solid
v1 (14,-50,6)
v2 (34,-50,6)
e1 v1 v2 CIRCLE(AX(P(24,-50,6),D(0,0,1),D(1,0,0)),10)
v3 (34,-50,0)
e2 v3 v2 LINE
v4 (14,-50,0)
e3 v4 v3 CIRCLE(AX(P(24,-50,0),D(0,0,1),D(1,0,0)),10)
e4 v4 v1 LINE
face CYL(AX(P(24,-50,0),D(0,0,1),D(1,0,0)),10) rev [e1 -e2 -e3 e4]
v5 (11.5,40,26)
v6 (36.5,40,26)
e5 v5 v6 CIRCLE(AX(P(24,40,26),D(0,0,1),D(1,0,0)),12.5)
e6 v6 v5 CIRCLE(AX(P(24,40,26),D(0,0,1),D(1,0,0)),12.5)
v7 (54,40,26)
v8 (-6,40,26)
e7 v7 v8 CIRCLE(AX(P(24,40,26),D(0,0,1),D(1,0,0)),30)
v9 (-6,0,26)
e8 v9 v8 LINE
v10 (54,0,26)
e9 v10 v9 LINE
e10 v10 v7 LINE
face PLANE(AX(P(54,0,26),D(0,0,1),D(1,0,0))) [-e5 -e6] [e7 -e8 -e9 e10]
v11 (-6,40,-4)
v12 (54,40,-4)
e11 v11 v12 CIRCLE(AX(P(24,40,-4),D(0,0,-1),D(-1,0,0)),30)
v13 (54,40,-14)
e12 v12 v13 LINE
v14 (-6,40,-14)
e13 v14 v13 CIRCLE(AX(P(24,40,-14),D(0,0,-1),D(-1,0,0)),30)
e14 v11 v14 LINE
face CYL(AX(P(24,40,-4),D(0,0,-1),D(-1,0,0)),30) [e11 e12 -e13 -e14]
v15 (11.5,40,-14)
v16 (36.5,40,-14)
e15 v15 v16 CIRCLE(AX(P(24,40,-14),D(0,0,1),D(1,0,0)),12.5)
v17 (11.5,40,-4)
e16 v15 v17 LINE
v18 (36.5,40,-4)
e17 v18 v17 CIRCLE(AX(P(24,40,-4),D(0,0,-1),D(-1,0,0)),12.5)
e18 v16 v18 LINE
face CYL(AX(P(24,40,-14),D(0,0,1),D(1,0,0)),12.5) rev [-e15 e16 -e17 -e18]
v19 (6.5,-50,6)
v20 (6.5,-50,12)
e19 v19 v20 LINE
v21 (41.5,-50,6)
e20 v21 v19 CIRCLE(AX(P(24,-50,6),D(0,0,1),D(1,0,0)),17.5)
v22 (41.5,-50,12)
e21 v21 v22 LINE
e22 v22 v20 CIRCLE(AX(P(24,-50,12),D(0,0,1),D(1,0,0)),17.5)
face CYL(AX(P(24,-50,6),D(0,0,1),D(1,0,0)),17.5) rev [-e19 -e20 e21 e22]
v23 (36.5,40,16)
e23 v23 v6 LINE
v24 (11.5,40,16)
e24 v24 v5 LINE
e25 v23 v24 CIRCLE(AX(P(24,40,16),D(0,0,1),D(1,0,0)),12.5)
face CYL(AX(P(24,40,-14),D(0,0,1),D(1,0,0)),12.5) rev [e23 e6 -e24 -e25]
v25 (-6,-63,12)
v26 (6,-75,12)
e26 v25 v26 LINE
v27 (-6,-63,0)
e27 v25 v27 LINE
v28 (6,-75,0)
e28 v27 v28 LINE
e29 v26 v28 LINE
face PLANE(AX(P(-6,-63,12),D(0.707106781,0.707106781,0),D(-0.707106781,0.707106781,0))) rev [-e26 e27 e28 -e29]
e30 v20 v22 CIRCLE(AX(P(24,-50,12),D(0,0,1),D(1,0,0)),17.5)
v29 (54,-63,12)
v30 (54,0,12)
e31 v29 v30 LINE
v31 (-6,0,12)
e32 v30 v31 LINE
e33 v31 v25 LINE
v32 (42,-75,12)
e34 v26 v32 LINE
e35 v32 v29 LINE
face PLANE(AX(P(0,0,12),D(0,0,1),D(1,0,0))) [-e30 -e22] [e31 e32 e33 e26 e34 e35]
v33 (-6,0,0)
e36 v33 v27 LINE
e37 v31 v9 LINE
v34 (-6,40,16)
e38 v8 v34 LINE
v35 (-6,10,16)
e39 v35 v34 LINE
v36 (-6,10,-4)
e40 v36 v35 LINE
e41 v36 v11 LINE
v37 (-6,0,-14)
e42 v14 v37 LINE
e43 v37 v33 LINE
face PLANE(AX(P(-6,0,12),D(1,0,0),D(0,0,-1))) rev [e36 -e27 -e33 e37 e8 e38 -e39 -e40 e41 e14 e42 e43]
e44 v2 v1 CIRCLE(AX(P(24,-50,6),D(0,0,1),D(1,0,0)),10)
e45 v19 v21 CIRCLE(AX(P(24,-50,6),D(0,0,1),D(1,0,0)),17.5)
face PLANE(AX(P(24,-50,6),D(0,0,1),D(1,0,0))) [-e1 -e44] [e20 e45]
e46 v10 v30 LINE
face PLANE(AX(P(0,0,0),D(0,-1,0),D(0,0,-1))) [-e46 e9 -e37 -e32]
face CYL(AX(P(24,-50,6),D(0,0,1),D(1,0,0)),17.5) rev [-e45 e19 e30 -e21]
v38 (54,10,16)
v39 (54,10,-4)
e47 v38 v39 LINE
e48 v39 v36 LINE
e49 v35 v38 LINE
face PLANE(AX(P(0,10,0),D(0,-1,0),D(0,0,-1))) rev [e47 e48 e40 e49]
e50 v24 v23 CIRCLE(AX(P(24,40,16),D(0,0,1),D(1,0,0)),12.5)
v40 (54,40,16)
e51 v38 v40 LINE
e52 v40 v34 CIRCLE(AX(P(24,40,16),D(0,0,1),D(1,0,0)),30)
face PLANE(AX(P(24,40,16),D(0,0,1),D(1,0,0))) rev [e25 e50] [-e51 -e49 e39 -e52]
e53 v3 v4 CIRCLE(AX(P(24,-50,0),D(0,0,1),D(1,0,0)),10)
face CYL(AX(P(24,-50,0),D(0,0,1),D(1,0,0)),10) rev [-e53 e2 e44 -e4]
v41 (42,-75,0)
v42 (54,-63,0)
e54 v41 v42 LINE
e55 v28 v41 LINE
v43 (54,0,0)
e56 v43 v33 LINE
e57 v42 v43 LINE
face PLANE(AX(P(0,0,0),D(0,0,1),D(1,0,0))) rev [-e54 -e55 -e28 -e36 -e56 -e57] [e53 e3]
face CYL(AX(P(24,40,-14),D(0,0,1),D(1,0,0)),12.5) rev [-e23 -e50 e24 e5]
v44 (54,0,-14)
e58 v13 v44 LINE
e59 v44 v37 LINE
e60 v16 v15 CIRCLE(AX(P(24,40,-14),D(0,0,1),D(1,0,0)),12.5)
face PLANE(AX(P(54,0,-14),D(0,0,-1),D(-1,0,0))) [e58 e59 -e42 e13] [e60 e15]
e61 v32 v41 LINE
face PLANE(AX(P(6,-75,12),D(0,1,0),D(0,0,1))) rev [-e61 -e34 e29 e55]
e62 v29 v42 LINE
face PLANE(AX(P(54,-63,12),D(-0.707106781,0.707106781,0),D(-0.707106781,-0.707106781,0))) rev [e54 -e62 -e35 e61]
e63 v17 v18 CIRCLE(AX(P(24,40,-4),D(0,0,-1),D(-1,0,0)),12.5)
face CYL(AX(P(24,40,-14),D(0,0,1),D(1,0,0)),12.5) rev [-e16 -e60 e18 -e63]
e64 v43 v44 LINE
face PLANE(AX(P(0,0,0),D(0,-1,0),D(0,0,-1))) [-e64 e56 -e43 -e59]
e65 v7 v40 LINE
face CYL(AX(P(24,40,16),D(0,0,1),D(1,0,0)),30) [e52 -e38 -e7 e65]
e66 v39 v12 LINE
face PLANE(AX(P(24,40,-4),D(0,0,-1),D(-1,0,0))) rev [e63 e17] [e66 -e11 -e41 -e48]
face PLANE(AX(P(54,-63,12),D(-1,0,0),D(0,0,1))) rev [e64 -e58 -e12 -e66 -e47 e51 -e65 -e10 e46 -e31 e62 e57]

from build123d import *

# Parameters (mm, degrees)
BASE_PLATE_DEPTH       = 12
CLEVIS_BODY_PROFILE_W  = 14
CLEVIS_BODY_PROFILE_H  = 40
CLEVIS_BODY_DEPTH      = 60
CLEVIS_BODY_2_DEPTH    = 60
LUG_1_BOSS_SKETCH_R    = 30
LUG_1_BOSS_DEPTH       = 10
LUG_1_TRIM_SKETCH_W    = 60
LUG_1_TRIM_SKETCH_H    = 4
LUG_1_TRIM_DEPTH       = 40
LUG_2_BOSS_SKETCH_R    = 30
LUG_2_BOSS_DEPTH       = 10
LUG_2_TRIM_SKETCH_W    = 60
LUG_2_TRIM_SKETCH_H    = 4
LUG_2_TRIM_DEPTH       = 40
CLEVIS_WEB_SKETCH_W    = 60
CLEVIS_WEB_SKETCH_H    = 20
CLEVIS_WEB_DEPTH       = 10
PIN_HOLE_SKETCH_R      = 12.5
PIN_HOLE_25_DEPTH      = 40
COUNTERBORE_SKETCH_R   = 17.5
COUNTERBORE_35X6_DEPTH = 6
MOUNTING_HOLE_SKETCH_R = 10
MOUNTING_HOLE_20_DEPTH = 6


with BuildPart() as part:
    # Base Plate Profile → Base Plate (new body)
    with BuildSketch(Plane.XY):
        Polygon((-6, 0), (-6, -63), (6, -75), (42, -75), (54, -63), (54, 0), align=None)
    extrude(amount=BASE_PLATE_DEPTH)



with BuildPart() as body_2:
    # Clevis Body Profile → Clevis Body (new body)
    with BuildSketch(Plane.ZY.offset(6)):
        with Locations((19, 20)):
            Rectangle(CLEVIS_BODY_PROFILE_W, CLEVIS_BODY_PROFILE_H)
    extrude(amount=-CLEVIS_BODY_DEPTH)

    # Lug 2 Boss Sketch → Lug 2 Boss (add)
    with BuildSketch(Plane.XY.offset(26)):
        with Locations((24, 40)):
            Circle(LUG_2_BOSS_SKETCH_R)
    extrude(amount=-LUG_2_BOSS_DEPTH)

    # Lug 2 Trim Sketch → Lug 2 Trim (cut)
    with BuildSketch(Plane(origin=(0, 40, 0), x_dir=(1, 0, 0), z_dir=(0, 1, 0))):
        with Locations((24, -14)):
            Rectangle(LUG_2_TRIM_SKETCH_W, LUG_2_TRIM_SKETCH_H)
    extrude(amount=-LUG_2_TRIM_DEPTH, mode=Mode.SUBTRACT)


with BuildPart() as body_3:
    # Clevis Body Profile → Clevis Body 2 (new body)
    with BuildSketch(Plane.ZY.offset(6)):
        with Locations((-7, 20)):
            Rectangle(CLEVIS_BODY_PROFILE_W, CLEVIS_BODY_PROFILE_H)
    extrude(amount=-CLEVIS_BODY_2_DEPTH)

    # Lug 1 Boss Sketch → Lug 1 Boss (add)
    with BuildSketch(Plane(origin=(0, 0, -14), x_dir=(-1, 0, 0), z_dir=(0, 0, -1))):
        with Locations((-24, 40)):
            Circle(LUG_1_BOSS_SKETCH_R)
    extrude(amount=-LUG_1_BOSS_DEPTH)

    # Lug 1 Trim Sketch → Lug 1 Trim (cut)
    with BuildSketch(Plane(origin=(0, 40, 0), x_dir=(1, 0, 0), z_dir=(0, 1, 0))):
        with Locations((24, 2)):
            Rectangle(LUG_1_TRIM_SKETCH_W, LUG_1_TRIM_SKETCH_H)
    extrude(amount=-LUG_1_TRIM_DEPTH, mode=Mode.SUBTRACT)


with BuildPart() as part_1:
    add(part.part)

    add(body_2.part)  # Clevis Web merges body 2

    add(body_3.part)  # Clevis Web merges body 3
    # Clevis Web Sketch → Clevis Web (add)
    with BuildSketch(Plane(origin=(0, 0, 0), x_dir=(1, 0, 0), z_dir=(0, 1, 0))):
        with Locations((24, -6)):
            Rectangle(CLEVIS_WEB_SKETCH_W, CLEVIS_WEB_SKETCH_H)
    extrude(amount=CLEVIS_WEB_DEPTH)

    # Pin Hole Sketch → Pin Hole Ø25 (cut)
    with BuildSketch(Plane.XY.offset(26)):
        with Locations((24, 40)):
            Circle(PIN_HOLE_SKETCH_R)
    extrude(amount=-PIN_HOLE_25_DEPTH, mode=Mode.SUBTRACT)

    # Counterbore Sketch → Counterbore Ø35x6 (cut)
    with BuildSketch(Plane.XY.offset(12)):
        with Locations((24, -50)):
            Circle(COUNTERBORE_SKETCH_R)
    extrude(amount=-COUNTERBORE_35X6_DEPTH, mode=Mode.SUBTRACT)

    # Mounting Hole Sketch → Mounting Hole Ø20 (cut)
    with BuildSketch(Plane.XY.offset(6)):
        with Locations((24, -50)):
            Circle(MOUNTING_HOLE_SKETCH_R)
    extrude(amount=-MOUNTING_HOLE_20_DEPTH, mode=Mode.SUBTRACT)


solid = part_1.part
